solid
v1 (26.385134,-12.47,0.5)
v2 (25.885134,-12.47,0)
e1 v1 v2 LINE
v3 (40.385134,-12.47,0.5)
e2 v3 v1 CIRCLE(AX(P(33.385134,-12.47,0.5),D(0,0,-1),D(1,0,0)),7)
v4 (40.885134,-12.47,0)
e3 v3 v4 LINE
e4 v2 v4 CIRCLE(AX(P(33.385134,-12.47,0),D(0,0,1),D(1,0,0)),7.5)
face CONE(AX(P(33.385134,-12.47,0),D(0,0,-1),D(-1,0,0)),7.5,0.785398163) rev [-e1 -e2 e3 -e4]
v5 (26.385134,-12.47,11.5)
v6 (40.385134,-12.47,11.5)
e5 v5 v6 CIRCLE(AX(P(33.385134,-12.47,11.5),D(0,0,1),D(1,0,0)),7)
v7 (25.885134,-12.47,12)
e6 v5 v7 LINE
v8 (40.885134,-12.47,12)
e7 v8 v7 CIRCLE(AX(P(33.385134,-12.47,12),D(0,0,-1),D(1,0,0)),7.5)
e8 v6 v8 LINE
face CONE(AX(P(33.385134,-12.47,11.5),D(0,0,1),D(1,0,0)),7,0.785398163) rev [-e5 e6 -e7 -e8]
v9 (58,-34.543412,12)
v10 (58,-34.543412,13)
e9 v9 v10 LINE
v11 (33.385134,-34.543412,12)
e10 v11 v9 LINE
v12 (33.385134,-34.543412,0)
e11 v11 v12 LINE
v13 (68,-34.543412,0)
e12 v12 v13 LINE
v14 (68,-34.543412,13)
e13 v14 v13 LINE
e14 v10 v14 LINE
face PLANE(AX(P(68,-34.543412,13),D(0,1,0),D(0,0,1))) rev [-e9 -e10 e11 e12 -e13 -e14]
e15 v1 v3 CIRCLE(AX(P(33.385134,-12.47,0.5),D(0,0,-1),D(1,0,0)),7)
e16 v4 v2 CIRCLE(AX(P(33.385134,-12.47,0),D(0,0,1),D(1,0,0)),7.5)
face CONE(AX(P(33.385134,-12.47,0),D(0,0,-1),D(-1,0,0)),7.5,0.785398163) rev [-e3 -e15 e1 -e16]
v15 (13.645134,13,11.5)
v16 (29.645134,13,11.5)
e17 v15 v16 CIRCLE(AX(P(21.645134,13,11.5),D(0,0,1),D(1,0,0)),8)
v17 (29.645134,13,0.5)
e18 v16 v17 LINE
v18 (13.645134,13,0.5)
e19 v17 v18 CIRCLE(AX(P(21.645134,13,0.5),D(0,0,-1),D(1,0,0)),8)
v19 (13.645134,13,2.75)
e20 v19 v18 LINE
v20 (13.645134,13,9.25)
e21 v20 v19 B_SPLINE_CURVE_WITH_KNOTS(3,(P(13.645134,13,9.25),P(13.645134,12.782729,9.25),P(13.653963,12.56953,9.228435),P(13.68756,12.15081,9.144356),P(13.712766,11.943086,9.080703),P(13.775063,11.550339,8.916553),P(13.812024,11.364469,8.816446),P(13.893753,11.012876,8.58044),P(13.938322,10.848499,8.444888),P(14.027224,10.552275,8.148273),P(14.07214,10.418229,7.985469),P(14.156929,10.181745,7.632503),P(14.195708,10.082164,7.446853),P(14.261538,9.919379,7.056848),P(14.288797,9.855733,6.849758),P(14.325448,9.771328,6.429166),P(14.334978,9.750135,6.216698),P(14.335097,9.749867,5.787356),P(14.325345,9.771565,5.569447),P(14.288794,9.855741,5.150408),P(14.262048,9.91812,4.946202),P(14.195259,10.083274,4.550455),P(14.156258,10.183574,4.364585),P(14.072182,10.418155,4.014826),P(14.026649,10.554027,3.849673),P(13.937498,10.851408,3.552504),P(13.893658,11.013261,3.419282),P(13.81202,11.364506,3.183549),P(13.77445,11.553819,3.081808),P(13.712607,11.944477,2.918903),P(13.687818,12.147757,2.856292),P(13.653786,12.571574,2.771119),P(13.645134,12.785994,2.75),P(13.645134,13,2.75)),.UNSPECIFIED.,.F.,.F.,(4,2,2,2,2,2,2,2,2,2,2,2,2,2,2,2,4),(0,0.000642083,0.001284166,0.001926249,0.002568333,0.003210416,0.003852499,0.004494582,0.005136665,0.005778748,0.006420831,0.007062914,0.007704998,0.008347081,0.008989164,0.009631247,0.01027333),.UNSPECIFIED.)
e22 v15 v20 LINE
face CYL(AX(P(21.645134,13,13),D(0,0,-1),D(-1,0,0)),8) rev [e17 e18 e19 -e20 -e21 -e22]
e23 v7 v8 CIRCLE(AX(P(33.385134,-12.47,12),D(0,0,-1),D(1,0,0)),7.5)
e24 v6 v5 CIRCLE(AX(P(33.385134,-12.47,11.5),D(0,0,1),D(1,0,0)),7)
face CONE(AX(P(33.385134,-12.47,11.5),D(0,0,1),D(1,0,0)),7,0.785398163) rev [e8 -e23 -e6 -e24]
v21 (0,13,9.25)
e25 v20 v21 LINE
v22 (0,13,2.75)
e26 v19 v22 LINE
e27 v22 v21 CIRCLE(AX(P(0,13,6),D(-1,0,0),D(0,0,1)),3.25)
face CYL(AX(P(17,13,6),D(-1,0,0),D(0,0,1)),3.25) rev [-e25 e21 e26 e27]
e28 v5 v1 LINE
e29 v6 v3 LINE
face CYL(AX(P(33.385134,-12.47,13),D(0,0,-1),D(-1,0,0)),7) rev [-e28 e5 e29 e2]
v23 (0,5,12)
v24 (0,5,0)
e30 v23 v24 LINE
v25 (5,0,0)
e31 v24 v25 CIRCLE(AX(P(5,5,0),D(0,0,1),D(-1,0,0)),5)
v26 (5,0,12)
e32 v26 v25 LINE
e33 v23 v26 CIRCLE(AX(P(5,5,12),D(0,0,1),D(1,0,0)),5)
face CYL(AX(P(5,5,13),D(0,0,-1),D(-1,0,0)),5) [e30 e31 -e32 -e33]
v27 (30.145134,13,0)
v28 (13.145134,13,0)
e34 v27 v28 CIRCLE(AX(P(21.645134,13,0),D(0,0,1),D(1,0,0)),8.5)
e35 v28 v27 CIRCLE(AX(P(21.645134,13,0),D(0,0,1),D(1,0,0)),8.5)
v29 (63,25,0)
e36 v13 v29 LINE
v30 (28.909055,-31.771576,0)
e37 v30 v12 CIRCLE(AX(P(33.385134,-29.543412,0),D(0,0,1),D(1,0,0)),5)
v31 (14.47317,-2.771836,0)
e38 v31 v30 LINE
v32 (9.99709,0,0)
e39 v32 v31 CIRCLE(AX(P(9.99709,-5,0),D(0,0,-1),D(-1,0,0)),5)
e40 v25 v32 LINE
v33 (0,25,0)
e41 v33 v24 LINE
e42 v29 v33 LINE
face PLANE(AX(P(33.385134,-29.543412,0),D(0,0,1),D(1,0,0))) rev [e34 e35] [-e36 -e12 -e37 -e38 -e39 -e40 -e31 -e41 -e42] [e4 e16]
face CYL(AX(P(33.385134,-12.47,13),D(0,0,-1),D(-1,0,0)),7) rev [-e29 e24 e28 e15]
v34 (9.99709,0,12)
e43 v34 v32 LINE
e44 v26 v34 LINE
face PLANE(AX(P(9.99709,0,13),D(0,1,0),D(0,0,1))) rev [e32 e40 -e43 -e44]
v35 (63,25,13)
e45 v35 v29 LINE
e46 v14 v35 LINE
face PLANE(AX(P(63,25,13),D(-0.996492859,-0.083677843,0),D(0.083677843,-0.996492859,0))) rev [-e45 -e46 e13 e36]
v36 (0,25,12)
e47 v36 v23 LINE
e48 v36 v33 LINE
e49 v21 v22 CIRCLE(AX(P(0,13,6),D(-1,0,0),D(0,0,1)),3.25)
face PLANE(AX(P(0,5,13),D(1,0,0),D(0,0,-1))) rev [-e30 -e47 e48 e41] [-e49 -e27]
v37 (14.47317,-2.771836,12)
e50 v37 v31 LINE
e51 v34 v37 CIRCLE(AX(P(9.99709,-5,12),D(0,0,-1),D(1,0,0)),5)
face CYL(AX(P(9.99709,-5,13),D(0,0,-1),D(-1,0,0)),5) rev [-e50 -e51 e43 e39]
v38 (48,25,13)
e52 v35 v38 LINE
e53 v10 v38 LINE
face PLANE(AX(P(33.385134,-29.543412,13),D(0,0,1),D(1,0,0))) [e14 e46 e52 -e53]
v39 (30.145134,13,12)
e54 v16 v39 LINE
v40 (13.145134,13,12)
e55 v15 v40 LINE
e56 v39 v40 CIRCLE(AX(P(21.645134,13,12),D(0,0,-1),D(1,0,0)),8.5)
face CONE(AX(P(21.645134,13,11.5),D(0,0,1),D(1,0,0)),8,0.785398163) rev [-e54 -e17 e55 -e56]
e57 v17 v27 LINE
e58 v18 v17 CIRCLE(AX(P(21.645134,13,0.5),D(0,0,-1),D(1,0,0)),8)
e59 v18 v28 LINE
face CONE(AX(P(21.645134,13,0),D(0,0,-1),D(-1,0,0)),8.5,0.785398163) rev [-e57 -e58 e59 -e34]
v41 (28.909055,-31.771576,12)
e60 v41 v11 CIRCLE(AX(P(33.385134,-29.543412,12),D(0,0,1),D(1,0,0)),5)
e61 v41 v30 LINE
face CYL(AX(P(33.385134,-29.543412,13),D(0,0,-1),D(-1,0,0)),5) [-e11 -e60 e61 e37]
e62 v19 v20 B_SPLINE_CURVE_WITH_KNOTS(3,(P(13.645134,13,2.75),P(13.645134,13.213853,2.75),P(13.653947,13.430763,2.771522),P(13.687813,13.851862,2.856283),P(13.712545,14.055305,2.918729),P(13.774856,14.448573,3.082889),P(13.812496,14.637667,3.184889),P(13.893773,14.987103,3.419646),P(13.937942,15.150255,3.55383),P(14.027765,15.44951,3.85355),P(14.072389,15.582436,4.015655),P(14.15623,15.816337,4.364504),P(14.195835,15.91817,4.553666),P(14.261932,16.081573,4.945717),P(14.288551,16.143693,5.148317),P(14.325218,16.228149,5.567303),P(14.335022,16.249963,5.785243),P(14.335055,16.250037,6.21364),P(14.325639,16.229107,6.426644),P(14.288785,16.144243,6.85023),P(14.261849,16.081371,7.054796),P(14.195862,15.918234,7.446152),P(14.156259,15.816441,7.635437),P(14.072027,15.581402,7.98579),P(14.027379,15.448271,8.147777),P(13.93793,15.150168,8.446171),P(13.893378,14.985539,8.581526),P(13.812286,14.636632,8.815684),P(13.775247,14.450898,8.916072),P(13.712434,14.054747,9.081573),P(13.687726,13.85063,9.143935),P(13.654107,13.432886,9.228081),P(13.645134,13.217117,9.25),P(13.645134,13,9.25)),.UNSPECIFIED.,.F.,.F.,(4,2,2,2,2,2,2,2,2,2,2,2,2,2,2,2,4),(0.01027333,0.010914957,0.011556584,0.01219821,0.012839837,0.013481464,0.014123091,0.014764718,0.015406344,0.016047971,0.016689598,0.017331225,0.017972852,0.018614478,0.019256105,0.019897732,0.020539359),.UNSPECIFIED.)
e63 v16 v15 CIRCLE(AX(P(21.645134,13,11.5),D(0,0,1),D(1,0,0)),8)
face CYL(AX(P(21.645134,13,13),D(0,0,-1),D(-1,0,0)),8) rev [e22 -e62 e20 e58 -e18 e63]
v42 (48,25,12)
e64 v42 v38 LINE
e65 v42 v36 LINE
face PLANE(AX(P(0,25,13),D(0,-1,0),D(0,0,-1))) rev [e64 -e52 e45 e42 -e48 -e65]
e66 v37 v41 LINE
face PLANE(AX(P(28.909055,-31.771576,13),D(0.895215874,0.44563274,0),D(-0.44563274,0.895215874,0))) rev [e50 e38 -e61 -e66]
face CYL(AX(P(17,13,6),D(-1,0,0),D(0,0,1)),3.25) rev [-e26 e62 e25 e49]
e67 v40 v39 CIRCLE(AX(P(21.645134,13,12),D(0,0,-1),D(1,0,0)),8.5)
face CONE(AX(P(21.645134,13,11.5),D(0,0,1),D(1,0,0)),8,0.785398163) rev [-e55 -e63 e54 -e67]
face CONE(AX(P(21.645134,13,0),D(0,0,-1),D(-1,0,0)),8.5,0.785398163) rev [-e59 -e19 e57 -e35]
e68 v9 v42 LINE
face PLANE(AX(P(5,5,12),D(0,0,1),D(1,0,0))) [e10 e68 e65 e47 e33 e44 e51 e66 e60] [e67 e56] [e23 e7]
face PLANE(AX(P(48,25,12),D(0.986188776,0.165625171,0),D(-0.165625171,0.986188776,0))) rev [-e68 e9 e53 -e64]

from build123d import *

# Parameters (mm, degrees)
SKETCH1_R           = 8
SKETCH1_R_2         = 7
BOSS_EXTRUDE1_DEPTH = 13
CUT_EXTRUDE1_START  = -1
CUT_EXTRUDE1_DEPTH  = 1
CHAMFER2_SIZE       = 0.5
SKETCH3_R           = 3.25
CUT_EXTRUDE2_DEPTH  = 17


with BuildPart() as part:
    # Sketch1 → Boss-Extrude1 (new body)
    with BuildSketch(Plane.XY):
        with BuildLine():
            Line((0, 5), (0, 25))
            Line((0, 25), (63, 25))
            Line((63, 25), (68, -34.543411946))
            Line((68, -34.543411946), (33.385133941, -34.543411946))
            ThreePointArc((33.385133941, -34.543411946), (30.752722356, -33.794342344), (28.909054571, -31.771575646))
            Line((28.909054571, -31.771575646), (14.473169684, -2.7718363))
            ThreePointArc((14.473169684, -2.7718363), (12.629501898, -0.749069602), (9.997090314, 0))
            Line((9.997090314, 0), (5, 0))
            ThreePointArc((5, 0), (1.464466094, 1.464466094), (0, 5))
        make_face()
        with Locations(Location((21.645133941, 13, 0), (0, 0, 180))):
            Circle(SKETCH1_R, mode=Mode.SUBTRACT)
        with Locations(Location((33.385133941, -12.47, 0), (0, 0, 180))):
            Circle(SKETCH1_R_2, mode=Mode.SUBTRACT)
    extrude(amount=BOSS_EXTRUDE1_DEPTH)

    # Sketch2 → Cut-Extrude1 (cut)
    with BuildSketch(Plane.XY.offset(13).offset(CUT_EXTRUDE1_START)):
        with BuildLine():
            Line((48, 25), (58, -34.543411946))
            Line((58, -34.543411946), (33.385133941, -34.543411946))
            ThreePointArc((33.385133941, -34.543411946), (30.752722356, -33.794342344), (28.909054571, -31.771575646))
            Line((28.909054571, -31.771575646), (14.473169684, -2.7718363))
            ThreePointArc((14.473169684, -2.7718363), (12.629501898, -0.749069602), (9.997090314, 0))
            Line((9.997090314, 0), (5, 0))
            ThreePointArc((5, 0), (1.464466094, 1.464466094), (0, 5))
            Line((0, 5), (0, 25))
            Line((0, 25), (48, 25))
        make_face()
    extrude(amount=CUT_EXTRUDE1_DEPTH, mode=Mode.SUBTRACT)

    # Chamfer2
    chamfer2_edges = [part.edges().sort_by_distance(p)[0] for p in [
        (29.645133941, 13, 0),
        (40.385133941, -12.47, 0),
        (29.645133941, 13, 12),
        (40.385133941, -12.47, 12),
    ]]
    chamfer(chamfer2_edges, length=CHAMFER2_SIZE)

    # Sketch3 → Cut-Extrude2 (cut)
    with BuildSketch(Plane.ZY):
        with Locations((6, 13)):
            Circle(SKETCH3_R)
    extrude(amount=-CUT_EXTRUDE2_DEPTH, mode=Mode.SUBTRACT)


solid = part.part
